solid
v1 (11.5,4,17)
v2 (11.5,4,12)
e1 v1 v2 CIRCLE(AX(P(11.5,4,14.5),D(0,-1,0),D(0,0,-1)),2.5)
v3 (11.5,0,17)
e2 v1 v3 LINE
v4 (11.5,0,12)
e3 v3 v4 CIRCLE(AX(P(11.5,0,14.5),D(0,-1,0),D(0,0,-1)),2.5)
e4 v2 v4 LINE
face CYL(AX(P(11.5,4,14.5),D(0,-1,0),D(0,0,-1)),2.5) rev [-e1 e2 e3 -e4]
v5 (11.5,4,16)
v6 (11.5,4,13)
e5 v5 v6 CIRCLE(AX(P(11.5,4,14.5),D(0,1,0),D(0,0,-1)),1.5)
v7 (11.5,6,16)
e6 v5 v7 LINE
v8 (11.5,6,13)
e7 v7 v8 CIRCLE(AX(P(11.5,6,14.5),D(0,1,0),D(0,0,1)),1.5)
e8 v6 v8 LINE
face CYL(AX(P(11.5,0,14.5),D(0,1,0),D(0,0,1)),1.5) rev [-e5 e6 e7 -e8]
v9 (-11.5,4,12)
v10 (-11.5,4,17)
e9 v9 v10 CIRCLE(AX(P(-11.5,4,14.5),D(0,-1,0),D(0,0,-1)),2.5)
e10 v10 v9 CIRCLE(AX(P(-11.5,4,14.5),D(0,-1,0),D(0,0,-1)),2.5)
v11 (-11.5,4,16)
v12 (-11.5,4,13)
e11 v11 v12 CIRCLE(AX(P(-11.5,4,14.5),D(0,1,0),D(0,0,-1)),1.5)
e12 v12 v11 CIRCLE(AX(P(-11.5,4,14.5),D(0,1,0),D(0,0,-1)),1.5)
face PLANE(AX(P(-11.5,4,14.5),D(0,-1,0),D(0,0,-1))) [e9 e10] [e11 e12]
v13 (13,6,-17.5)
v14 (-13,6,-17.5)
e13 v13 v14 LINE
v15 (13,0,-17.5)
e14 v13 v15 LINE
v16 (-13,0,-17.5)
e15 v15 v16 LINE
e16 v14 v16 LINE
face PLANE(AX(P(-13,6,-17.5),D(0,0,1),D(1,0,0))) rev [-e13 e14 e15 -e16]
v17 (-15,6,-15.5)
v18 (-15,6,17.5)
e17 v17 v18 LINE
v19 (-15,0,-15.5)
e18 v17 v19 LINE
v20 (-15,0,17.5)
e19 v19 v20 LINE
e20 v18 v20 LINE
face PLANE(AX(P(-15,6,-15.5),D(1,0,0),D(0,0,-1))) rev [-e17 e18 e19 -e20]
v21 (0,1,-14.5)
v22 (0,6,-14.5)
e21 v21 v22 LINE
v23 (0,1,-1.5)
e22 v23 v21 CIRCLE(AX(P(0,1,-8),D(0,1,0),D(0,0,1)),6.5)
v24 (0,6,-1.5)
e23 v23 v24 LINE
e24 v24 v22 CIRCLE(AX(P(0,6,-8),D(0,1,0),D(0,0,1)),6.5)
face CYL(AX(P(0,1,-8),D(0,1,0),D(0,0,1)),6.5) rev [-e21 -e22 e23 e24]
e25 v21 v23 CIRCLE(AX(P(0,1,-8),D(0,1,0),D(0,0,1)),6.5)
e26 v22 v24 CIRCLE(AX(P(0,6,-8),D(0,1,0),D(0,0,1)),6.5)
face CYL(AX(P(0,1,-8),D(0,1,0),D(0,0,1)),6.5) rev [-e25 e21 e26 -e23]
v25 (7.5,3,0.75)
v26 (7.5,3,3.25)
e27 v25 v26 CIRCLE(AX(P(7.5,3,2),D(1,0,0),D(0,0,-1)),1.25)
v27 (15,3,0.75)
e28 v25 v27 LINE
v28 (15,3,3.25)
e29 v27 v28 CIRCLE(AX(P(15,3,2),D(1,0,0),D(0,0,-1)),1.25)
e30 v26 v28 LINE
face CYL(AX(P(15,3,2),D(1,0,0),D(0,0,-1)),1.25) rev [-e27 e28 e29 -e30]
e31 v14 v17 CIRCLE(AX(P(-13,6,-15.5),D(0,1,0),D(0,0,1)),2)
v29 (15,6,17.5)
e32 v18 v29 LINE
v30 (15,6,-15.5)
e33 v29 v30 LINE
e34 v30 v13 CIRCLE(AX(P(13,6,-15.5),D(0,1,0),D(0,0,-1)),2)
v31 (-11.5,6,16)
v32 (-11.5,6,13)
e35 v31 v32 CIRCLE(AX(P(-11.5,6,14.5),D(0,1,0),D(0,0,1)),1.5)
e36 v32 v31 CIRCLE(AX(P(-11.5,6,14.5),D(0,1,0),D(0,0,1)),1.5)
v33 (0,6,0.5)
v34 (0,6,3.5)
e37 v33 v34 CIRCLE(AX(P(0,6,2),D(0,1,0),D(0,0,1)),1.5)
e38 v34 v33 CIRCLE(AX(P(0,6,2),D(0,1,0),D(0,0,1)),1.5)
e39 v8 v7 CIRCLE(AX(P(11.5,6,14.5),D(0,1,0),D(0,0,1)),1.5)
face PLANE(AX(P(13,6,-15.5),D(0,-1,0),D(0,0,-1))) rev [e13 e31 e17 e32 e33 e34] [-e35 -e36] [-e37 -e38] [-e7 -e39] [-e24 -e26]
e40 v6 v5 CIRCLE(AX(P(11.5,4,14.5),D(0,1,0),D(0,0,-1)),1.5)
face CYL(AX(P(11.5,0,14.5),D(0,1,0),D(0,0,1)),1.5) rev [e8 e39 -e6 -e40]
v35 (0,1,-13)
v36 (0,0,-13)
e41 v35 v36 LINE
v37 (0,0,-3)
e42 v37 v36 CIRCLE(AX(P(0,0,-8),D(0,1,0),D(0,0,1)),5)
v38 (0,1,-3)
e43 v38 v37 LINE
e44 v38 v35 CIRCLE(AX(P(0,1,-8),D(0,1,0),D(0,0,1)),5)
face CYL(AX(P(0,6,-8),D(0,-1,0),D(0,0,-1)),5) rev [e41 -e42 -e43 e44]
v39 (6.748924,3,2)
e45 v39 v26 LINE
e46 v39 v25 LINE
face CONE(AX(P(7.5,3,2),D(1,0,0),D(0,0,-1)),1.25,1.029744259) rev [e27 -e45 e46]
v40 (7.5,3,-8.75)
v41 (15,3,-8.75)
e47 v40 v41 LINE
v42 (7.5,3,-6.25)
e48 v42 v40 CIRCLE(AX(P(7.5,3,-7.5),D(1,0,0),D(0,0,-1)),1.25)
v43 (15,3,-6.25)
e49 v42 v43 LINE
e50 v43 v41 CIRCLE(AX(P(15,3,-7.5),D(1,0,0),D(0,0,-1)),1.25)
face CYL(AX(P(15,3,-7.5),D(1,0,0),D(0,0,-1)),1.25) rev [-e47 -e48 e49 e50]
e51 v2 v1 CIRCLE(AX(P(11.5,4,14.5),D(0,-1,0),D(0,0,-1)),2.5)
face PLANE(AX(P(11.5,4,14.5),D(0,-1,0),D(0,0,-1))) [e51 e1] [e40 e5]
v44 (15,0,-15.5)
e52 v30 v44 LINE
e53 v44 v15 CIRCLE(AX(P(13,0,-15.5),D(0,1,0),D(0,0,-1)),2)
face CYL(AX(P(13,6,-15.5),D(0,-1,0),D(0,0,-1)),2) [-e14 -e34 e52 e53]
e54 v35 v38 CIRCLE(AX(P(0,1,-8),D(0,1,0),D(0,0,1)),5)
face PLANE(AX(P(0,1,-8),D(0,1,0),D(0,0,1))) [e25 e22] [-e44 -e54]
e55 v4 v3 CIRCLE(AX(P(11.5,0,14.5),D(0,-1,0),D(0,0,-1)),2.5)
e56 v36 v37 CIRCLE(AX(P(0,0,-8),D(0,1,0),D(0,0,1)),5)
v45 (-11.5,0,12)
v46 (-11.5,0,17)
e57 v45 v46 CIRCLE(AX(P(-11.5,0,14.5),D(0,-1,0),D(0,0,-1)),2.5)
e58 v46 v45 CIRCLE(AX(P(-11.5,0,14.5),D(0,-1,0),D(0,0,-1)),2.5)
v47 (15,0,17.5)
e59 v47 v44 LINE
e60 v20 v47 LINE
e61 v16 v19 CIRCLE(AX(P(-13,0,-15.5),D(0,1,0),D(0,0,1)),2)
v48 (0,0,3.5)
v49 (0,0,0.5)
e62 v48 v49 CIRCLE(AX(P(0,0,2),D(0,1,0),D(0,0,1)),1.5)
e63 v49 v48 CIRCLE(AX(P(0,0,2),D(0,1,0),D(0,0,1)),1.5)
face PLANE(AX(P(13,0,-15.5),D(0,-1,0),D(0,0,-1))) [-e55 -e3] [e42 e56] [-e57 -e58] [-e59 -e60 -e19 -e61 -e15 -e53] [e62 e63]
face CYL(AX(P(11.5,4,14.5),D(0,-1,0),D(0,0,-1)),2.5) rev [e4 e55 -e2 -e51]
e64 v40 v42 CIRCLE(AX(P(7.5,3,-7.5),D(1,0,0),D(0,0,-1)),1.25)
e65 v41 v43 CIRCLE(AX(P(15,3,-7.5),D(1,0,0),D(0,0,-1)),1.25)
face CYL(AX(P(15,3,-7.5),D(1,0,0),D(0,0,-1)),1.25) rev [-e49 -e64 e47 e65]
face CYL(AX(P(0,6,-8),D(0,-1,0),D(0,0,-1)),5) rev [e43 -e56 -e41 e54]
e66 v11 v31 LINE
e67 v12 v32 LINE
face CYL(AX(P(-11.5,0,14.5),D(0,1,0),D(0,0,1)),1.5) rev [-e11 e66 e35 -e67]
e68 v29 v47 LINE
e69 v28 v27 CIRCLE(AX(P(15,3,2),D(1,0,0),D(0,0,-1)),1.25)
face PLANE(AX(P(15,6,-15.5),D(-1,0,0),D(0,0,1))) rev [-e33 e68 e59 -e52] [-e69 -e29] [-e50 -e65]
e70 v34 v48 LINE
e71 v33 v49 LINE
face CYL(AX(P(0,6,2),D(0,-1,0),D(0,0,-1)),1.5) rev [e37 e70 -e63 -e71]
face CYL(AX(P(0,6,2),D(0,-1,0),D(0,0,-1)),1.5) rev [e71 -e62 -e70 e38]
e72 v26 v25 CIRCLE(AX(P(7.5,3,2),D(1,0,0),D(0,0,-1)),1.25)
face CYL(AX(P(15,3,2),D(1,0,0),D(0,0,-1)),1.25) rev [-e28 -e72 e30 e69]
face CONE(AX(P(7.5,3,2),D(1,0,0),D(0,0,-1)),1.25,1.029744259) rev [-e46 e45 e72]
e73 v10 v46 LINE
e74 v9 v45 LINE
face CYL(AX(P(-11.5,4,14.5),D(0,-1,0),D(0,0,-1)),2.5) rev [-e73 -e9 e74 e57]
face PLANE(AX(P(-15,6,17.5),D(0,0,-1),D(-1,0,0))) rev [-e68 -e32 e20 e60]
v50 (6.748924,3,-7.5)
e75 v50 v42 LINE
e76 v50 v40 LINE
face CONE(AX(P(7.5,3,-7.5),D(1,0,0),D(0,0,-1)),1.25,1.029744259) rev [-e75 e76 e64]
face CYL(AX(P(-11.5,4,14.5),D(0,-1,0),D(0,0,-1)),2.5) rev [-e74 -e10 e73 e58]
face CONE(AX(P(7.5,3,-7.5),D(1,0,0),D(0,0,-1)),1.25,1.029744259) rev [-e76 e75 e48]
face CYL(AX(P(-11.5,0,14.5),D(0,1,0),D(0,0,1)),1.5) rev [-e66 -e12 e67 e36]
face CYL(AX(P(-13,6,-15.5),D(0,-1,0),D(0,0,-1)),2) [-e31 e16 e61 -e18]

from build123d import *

# Parameters (mm, degrees)
SKETCH1_R             = 5
SKETCH1_R_2           = 1.5
BOSS_EXTRUDE1_DEPTH   = 6
SKETCH3_R             = 6.5
CUT_EXTRUDE1_DEPTH    = 5
SKETCH4_R             = 1.5
CUT_EXTRUDE2_DEPTH    = 24.817010728
SKETCH5_R             = 2.5
CUT_EXTRUDE3_DEPTH    = 4
SKETCH8_R             = 1
CUT_EXTRUDE6_DEPTH    = 2
M3_TAPPED_HOLE1_D     = 2.5
M3_TAPPED_HOLE1_DEPTH = 7.5
M3_TAPPED_HOLE1_TIP   = 0.751075774


with BuildPart() as part:
    # Sketch1 → Boss-Extrude1 (new body)
    with BuildSketch(Plane(origin=(0, 0, 0), x_dir=(1, 0, 0), z_dir=(0, 1, 0))):
        with BuildLine():
            Line((-13, 17.5), (13, 17.5))
            ThreePointArc((13, 17.5), (14.414213562, 16.914213562), (15, 15.5))
            Line((15, 15.5), (15, -17.5))
            Line((15, -17.5), (-15, -17.5))
            Line((-15, -17.5), (-15, 15.5))
            ThreePointArc((-15, 15.5), (-14.414213562, 16.914213562), (-13, 17.5))
        make_face()
        with Locations(Location((0, 8, 0), (0, 0, 270))):
            Circle(SKETCH1_R, mode=Mode.SUBTRACT)
        with Locations(Location((0, -2, 0), (0, 0, 270))):
            Circle(SKETCH1_R_2, mode=Mode.SUBTRACT)
    extrude(amount=BOSS_EXTRUDE1_DEPTH)

    # Sketch3 → Cut-Extrude1 (cut)
    with BuildSketch(Plane(origin=(0, 6, 0), x_dir=(1, 0, 0), z_dir=(0, 1, 0))):
        with Locations(Location((0, 8, 0), (0, 0, 270))):
            Circle(SKETCH3_R)
    extrude(amount=-CUT_EXTRUDE1_DEPTH, mode=Mode.SUBTRACT)

    # Sketch4 → Cut-Extrude2 (cut, through all)
    with BuildSketch(Plane(origin=(0, 6, 0), x_dir=(1, 0, 0), z_dir=(0, 1, 0))):
        with Locations(Location((-11.5, -14.5, 0), (0, 0, 270))):
            Circle(SKETCH4_R)
        with Locations(Location((11.5, -14.5, 0), (0, 0, 270))):
            Circle(SKETCH4_R)
    extrude(amount=-CUT_EXTRUDE2_DEPTH, mode=Mode.SUBTRACT)

    # Sketch5 → Cut-Extrude3 (cut)
    with BuildSketch(Plane.XZ):
        with Locations(Location((11.5, 14.5, 0), (0, 0, 270))):
            Circle(SKETCH5_R)
        with Locations(Location((-11.5, 14.5, 0), (0, 0, 270))):
            Circle(SKETCH5_R)
    extrude(amount=-CUT_EXTRUDE3_DEPTH, mode=Mode.SUBTRACT)

    # Sketch8 → Cut-Extrude6 (cut)
    with BuildSketch(Plane(origin=(15, 0, 0), x_dir=(0, 0, -1), z_dir=(1, 0, 0))):
        with Locations((-2, 3)):
            Circle(SKETCH8_R)
        with Locations((7.5, 3)):
            Circle(SKETCH8_R)
    extrude(amount=-CUT_EXTRUDE6_DEPTH, mode=Mode.SUBTRACT)

    # M3 Tapped Hole1
    with Locations(Plane(origin=(15, 0, 0), x_dir=(0, 0, -1), z_dir=(1, 0, 0))):
        with Locations((-2, 3), (7.5, 3)):
            Hole(M3_TAPPED_HOLE1_D / 2, depth=M3_TAPPED_HOLE1_DEPTH)
            with Locations((0, 0, -(M3_TAPPED_HOLE1_DEPTH + M3_TAPPED_HOLE1_TIP / 2))):  # 118° drill point
                Cone(0, M3_TAPPED_HOLE1_D / 2, M3_TAPPED_HOLE1_TIP, mode=Mode.SUBTRACT)


solid = part.part
